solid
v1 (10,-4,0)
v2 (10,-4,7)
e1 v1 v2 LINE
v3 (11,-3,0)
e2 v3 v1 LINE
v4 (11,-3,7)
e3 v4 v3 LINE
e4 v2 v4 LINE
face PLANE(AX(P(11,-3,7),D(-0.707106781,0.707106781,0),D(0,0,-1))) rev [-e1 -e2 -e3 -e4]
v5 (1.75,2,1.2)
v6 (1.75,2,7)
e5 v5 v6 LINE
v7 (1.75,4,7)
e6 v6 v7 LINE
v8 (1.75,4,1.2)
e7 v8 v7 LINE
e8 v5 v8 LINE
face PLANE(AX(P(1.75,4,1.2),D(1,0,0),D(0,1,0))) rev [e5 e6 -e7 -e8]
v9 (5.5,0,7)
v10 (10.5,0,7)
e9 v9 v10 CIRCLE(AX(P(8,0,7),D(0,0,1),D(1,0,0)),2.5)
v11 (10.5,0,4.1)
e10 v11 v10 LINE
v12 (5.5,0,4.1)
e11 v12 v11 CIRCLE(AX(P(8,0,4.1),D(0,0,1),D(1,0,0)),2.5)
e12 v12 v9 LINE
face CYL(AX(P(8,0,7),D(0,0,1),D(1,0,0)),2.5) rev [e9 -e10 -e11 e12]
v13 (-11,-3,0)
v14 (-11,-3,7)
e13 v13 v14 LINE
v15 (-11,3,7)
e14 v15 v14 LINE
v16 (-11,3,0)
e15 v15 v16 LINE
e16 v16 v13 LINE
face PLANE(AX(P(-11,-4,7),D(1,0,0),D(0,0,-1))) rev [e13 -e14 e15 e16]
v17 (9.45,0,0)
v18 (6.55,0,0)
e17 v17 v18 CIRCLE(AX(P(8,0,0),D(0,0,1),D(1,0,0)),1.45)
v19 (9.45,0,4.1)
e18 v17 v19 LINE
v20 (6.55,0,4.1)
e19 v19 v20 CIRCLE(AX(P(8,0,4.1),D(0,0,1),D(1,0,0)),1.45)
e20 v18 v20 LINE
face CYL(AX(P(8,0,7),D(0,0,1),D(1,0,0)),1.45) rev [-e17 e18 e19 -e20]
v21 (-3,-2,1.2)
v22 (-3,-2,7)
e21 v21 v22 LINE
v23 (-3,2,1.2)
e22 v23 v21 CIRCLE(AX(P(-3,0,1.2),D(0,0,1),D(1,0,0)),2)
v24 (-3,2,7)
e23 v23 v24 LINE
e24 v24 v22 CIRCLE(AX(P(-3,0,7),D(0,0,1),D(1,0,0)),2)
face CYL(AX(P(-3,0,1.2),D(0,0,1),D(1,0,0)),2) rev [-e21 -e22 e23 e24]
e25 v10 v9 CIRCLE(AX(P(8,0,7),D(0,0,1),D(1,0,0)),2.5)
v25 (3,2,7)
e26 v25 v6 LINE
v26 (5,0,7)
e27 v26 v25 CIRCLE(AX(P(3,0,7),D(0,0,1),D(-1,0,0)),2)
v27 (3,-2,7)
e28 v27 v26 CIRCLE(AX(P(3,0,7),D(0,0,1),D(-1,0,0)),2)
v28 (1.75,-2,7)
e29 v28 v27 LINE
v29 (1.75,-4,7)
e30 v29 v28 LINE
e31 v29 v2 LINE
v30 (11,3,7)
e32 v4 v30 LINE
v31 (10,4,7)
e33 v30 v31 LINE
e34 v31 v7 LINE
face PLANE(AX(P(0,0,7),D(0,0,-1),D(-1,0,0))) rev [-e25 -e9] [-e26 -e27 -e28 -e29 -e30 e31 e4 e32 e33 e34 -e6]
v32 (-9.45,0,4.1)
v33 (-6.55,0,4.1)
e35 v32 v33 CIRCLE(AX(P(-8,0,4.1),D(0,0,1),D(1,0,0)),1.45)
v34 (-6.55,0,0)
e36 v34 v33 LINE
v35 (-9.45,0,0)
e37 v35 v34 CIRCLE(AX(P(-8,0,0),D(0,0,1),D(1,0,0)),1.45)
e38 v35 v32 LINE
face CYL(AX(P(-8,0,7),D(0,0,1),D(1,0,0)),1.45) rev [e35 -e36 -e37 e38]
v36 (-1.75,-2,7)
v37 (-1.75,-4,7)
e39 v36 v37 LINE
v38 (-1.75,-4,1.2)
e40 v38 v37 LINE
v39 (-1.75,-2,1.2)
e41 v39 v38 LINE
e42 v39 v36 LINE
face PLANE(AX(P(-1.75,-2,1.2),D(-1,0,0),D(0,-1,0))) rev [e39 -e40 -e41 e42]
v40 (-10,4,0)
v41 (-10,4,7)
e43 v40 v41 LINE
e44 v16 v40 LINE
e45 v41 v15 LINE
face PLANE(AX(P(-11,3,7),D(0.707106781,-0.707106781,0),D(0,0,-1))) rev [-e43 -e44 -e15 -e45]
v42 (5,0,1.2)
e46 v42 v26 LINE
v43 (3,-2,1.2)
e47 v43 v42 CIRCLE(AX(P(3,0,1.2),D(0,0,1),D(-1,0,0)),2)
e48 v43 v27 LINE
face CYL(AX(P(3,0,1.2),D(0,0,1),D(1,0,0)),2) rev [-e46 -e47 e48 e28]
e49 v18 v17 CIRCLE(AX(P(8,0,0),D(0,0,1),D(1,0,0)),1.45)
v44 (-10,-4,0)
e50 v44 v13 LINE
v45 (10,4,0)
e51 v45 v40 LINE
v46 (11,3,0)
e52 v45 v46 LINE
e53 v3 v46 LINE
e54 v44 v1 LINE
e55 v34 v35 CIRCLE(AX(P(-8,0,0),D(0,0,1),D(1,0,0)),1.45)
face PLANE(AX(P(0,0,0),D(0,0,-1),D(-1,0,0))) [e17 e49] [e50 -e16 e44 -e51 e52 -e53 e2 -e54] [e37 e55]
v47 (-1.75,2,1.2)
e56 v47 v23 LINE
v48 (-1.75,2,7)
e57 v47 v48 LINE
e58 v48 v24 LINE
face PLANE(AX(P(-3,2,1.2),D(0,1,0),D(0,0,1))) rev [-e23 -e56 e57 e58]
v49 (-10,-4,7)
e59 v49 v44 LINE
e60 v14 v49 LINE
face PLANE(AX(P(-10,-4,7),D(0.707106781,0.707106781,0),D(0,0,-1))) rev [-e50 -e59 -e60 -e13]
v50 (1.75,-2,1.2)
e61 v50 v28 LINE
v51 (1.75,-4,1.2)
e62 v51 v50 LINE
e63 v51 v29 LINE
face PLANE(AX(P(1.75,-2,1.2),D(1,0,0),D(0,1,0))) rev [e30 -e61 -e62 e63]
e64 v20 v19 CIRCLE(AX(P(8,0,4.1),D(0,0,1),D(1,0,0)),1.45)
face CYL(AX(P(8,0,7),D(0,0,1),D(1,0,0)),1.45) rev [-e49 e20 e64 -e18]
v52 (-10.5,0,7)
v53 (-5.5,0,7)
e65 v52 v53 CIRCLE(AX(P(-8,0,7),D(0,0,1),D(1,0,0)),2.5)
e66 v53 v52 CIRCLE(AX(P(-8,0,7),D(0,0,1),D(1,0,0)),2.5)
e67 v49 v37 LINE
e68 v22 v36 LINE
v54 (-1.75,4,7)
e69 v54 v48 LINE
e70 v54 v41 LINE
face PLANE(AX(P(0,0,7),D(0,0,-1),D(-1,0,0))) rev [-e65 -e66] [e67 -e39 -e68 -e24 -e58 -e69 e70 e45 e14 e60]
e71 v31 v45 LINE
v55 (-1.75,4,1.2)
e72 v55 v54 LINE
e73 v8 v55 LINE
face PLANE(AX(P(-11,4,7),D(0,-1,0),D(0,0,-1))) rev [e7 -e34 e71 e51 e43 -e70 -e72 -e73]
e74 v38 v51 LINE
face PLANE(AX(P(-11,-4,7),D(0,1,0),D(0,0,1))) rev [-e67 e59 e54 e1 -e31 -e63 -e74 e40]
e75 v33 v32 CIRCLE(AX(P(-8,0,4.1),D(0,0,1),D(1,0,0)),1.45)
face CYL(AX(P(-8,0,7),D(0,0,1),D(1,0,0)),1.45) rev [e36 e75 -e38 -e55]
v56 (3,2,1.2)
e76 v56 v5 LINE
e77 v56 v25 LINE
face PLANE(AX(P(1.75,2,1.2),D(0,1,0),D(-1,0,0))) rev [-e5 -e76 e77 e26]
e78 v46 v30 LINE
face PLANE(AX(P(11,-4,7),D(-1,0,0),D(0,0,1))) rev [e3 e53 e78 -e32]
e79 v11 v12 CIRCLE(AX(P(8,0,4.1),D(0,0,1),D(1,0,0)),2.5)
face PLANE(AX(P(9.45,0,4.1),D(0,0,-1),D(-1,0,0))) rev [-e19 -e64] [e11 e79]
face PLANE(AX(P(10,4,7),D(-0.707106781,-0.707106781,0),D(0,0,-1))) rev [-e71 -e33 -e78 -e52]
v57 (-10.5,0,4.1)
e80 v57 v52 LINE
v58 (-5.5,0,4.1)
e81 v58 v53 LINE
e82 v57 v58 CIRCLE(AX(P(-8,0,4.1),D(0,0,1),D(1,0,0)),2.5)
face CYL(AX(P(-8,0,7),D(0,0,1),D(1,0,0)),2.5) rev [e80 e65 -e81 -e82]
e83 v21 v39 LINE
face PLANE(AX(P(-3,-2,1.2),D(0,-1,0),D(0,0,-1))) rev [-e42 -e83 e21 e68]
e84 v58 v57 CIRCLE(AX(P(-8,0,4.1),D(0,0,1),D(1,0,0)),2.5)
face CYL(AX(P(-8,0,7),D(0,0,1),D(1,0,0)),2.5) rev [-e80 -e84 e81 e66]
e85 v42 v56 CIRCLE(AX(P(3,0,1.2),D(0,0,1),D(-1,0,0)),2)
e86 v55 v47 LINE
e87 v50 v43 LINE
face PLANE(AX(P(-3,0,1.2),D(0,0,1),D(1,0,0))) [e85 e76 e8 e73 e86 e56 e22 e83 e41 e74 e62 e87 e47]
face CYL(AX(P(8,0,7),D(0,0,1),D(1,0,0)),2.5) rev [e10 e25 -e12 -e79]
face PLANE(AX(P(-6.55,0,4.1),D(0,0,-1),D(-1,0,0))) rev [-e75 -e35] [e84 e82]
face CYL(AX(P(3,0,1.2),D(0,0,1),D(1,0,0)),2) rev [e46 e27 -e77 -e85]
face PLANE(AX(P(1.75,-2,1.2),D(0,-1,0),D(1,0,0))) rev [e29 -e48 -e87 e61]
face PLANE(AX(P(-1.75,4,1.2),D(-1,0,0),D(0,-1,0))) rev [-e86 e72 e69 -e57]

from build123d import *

# Parameters (mm, degrees)
SKETCH1_W                                            = 22
SKETCH1_H                                            = 8
BOSS_EXTRUDE1_DEPTH                                  = 7
CUT_EXTRUDE1_DEPTH                                   = 5.8
CHAMFER1_SIZE                                        = 1
HOLE_SIZE_PER_SOCKET_HEAD_CAP_SCREW_TYPE_D           = 2.9
HOLE_SIZE_PER_SOCKET_HEAD_CAP_SCREW_TYPE_CBORE_D     = 5
HOLE_SIZE_PER_SOCKET_HEAD_CAP_SCREW_TYPE_CBORE_DEPTH = 2.9


with BuildPart() as part:
    # Sketch1 → Boss-Extrude1 (new body)
    with BuildSketch(Plane.XY):
        Rectangle(SKETCH1_W, SKETCH1_H)
    extrude(amount=BOSS_EXTRUDE1_DEPTH)

    # Sketch3 → Cut-Extrude1 (cut)
    with BuildSketch(Plane.XY.offset(7)):
        with BuildLine():
            Line((-3, 2), (-1.75, 2))
            Line((-1.75, 2), (-1.75, 4))
            Line((-1.75, 4), (1.75, 4))
            Line((1.75, 4), (1.75, 2))
            Line((1.75, 2), (3, 2))
            ThreePointArc((3, 2), (5, 0), (3, -2))
            Line((3, -2), (1.75, -2))
            Line((1.75, -2), (1.75, -4))
            Line((1.75, -4), (-1.75, -4))
            Line((-1.75, -4), (-1.75, -2))
            Line((-1.75, -2), (-3, -2))
            ThreePointArc((-3, -2), (-5, 0), (-3, 2))
        make_face()
    extrude(amount=-CUT_EXTRUDE1_DEPTH, mode=Mode.SUBTRACT)

    # Chamfer1
    chamfer1_edges = [part.edges().sort_by_distance(p)[0] for p in [
        (11, -4, 3.5),
        (-11, -4, 3.5),
        (-11, 4, 3.5),
        (11, 4, 3.5),
    ]]
    chamfer(chamfer1_edges, length=CHAMFER1_SIZE)

    # Hole size per socket head cap screw type 1 (through all)
    with Locations(Plane.XY.offset(7)):
        with Locations((-8, 0), (8, 0)):
            CounterBoreHole(HOLE_SIZE_PER_SOCKET_HEAD_CAP_SCREW_TYPE_D / 2, HOLE_SIZE_PER_SOCKET_HEAD_CAP_SCREW_TYPE_CBORE_D / 2, HOLE_SIZE_PER_SOCKET_HEAD_CAP_SCREW_TYPE_CBORE_DEPTH)


solid = part.part
